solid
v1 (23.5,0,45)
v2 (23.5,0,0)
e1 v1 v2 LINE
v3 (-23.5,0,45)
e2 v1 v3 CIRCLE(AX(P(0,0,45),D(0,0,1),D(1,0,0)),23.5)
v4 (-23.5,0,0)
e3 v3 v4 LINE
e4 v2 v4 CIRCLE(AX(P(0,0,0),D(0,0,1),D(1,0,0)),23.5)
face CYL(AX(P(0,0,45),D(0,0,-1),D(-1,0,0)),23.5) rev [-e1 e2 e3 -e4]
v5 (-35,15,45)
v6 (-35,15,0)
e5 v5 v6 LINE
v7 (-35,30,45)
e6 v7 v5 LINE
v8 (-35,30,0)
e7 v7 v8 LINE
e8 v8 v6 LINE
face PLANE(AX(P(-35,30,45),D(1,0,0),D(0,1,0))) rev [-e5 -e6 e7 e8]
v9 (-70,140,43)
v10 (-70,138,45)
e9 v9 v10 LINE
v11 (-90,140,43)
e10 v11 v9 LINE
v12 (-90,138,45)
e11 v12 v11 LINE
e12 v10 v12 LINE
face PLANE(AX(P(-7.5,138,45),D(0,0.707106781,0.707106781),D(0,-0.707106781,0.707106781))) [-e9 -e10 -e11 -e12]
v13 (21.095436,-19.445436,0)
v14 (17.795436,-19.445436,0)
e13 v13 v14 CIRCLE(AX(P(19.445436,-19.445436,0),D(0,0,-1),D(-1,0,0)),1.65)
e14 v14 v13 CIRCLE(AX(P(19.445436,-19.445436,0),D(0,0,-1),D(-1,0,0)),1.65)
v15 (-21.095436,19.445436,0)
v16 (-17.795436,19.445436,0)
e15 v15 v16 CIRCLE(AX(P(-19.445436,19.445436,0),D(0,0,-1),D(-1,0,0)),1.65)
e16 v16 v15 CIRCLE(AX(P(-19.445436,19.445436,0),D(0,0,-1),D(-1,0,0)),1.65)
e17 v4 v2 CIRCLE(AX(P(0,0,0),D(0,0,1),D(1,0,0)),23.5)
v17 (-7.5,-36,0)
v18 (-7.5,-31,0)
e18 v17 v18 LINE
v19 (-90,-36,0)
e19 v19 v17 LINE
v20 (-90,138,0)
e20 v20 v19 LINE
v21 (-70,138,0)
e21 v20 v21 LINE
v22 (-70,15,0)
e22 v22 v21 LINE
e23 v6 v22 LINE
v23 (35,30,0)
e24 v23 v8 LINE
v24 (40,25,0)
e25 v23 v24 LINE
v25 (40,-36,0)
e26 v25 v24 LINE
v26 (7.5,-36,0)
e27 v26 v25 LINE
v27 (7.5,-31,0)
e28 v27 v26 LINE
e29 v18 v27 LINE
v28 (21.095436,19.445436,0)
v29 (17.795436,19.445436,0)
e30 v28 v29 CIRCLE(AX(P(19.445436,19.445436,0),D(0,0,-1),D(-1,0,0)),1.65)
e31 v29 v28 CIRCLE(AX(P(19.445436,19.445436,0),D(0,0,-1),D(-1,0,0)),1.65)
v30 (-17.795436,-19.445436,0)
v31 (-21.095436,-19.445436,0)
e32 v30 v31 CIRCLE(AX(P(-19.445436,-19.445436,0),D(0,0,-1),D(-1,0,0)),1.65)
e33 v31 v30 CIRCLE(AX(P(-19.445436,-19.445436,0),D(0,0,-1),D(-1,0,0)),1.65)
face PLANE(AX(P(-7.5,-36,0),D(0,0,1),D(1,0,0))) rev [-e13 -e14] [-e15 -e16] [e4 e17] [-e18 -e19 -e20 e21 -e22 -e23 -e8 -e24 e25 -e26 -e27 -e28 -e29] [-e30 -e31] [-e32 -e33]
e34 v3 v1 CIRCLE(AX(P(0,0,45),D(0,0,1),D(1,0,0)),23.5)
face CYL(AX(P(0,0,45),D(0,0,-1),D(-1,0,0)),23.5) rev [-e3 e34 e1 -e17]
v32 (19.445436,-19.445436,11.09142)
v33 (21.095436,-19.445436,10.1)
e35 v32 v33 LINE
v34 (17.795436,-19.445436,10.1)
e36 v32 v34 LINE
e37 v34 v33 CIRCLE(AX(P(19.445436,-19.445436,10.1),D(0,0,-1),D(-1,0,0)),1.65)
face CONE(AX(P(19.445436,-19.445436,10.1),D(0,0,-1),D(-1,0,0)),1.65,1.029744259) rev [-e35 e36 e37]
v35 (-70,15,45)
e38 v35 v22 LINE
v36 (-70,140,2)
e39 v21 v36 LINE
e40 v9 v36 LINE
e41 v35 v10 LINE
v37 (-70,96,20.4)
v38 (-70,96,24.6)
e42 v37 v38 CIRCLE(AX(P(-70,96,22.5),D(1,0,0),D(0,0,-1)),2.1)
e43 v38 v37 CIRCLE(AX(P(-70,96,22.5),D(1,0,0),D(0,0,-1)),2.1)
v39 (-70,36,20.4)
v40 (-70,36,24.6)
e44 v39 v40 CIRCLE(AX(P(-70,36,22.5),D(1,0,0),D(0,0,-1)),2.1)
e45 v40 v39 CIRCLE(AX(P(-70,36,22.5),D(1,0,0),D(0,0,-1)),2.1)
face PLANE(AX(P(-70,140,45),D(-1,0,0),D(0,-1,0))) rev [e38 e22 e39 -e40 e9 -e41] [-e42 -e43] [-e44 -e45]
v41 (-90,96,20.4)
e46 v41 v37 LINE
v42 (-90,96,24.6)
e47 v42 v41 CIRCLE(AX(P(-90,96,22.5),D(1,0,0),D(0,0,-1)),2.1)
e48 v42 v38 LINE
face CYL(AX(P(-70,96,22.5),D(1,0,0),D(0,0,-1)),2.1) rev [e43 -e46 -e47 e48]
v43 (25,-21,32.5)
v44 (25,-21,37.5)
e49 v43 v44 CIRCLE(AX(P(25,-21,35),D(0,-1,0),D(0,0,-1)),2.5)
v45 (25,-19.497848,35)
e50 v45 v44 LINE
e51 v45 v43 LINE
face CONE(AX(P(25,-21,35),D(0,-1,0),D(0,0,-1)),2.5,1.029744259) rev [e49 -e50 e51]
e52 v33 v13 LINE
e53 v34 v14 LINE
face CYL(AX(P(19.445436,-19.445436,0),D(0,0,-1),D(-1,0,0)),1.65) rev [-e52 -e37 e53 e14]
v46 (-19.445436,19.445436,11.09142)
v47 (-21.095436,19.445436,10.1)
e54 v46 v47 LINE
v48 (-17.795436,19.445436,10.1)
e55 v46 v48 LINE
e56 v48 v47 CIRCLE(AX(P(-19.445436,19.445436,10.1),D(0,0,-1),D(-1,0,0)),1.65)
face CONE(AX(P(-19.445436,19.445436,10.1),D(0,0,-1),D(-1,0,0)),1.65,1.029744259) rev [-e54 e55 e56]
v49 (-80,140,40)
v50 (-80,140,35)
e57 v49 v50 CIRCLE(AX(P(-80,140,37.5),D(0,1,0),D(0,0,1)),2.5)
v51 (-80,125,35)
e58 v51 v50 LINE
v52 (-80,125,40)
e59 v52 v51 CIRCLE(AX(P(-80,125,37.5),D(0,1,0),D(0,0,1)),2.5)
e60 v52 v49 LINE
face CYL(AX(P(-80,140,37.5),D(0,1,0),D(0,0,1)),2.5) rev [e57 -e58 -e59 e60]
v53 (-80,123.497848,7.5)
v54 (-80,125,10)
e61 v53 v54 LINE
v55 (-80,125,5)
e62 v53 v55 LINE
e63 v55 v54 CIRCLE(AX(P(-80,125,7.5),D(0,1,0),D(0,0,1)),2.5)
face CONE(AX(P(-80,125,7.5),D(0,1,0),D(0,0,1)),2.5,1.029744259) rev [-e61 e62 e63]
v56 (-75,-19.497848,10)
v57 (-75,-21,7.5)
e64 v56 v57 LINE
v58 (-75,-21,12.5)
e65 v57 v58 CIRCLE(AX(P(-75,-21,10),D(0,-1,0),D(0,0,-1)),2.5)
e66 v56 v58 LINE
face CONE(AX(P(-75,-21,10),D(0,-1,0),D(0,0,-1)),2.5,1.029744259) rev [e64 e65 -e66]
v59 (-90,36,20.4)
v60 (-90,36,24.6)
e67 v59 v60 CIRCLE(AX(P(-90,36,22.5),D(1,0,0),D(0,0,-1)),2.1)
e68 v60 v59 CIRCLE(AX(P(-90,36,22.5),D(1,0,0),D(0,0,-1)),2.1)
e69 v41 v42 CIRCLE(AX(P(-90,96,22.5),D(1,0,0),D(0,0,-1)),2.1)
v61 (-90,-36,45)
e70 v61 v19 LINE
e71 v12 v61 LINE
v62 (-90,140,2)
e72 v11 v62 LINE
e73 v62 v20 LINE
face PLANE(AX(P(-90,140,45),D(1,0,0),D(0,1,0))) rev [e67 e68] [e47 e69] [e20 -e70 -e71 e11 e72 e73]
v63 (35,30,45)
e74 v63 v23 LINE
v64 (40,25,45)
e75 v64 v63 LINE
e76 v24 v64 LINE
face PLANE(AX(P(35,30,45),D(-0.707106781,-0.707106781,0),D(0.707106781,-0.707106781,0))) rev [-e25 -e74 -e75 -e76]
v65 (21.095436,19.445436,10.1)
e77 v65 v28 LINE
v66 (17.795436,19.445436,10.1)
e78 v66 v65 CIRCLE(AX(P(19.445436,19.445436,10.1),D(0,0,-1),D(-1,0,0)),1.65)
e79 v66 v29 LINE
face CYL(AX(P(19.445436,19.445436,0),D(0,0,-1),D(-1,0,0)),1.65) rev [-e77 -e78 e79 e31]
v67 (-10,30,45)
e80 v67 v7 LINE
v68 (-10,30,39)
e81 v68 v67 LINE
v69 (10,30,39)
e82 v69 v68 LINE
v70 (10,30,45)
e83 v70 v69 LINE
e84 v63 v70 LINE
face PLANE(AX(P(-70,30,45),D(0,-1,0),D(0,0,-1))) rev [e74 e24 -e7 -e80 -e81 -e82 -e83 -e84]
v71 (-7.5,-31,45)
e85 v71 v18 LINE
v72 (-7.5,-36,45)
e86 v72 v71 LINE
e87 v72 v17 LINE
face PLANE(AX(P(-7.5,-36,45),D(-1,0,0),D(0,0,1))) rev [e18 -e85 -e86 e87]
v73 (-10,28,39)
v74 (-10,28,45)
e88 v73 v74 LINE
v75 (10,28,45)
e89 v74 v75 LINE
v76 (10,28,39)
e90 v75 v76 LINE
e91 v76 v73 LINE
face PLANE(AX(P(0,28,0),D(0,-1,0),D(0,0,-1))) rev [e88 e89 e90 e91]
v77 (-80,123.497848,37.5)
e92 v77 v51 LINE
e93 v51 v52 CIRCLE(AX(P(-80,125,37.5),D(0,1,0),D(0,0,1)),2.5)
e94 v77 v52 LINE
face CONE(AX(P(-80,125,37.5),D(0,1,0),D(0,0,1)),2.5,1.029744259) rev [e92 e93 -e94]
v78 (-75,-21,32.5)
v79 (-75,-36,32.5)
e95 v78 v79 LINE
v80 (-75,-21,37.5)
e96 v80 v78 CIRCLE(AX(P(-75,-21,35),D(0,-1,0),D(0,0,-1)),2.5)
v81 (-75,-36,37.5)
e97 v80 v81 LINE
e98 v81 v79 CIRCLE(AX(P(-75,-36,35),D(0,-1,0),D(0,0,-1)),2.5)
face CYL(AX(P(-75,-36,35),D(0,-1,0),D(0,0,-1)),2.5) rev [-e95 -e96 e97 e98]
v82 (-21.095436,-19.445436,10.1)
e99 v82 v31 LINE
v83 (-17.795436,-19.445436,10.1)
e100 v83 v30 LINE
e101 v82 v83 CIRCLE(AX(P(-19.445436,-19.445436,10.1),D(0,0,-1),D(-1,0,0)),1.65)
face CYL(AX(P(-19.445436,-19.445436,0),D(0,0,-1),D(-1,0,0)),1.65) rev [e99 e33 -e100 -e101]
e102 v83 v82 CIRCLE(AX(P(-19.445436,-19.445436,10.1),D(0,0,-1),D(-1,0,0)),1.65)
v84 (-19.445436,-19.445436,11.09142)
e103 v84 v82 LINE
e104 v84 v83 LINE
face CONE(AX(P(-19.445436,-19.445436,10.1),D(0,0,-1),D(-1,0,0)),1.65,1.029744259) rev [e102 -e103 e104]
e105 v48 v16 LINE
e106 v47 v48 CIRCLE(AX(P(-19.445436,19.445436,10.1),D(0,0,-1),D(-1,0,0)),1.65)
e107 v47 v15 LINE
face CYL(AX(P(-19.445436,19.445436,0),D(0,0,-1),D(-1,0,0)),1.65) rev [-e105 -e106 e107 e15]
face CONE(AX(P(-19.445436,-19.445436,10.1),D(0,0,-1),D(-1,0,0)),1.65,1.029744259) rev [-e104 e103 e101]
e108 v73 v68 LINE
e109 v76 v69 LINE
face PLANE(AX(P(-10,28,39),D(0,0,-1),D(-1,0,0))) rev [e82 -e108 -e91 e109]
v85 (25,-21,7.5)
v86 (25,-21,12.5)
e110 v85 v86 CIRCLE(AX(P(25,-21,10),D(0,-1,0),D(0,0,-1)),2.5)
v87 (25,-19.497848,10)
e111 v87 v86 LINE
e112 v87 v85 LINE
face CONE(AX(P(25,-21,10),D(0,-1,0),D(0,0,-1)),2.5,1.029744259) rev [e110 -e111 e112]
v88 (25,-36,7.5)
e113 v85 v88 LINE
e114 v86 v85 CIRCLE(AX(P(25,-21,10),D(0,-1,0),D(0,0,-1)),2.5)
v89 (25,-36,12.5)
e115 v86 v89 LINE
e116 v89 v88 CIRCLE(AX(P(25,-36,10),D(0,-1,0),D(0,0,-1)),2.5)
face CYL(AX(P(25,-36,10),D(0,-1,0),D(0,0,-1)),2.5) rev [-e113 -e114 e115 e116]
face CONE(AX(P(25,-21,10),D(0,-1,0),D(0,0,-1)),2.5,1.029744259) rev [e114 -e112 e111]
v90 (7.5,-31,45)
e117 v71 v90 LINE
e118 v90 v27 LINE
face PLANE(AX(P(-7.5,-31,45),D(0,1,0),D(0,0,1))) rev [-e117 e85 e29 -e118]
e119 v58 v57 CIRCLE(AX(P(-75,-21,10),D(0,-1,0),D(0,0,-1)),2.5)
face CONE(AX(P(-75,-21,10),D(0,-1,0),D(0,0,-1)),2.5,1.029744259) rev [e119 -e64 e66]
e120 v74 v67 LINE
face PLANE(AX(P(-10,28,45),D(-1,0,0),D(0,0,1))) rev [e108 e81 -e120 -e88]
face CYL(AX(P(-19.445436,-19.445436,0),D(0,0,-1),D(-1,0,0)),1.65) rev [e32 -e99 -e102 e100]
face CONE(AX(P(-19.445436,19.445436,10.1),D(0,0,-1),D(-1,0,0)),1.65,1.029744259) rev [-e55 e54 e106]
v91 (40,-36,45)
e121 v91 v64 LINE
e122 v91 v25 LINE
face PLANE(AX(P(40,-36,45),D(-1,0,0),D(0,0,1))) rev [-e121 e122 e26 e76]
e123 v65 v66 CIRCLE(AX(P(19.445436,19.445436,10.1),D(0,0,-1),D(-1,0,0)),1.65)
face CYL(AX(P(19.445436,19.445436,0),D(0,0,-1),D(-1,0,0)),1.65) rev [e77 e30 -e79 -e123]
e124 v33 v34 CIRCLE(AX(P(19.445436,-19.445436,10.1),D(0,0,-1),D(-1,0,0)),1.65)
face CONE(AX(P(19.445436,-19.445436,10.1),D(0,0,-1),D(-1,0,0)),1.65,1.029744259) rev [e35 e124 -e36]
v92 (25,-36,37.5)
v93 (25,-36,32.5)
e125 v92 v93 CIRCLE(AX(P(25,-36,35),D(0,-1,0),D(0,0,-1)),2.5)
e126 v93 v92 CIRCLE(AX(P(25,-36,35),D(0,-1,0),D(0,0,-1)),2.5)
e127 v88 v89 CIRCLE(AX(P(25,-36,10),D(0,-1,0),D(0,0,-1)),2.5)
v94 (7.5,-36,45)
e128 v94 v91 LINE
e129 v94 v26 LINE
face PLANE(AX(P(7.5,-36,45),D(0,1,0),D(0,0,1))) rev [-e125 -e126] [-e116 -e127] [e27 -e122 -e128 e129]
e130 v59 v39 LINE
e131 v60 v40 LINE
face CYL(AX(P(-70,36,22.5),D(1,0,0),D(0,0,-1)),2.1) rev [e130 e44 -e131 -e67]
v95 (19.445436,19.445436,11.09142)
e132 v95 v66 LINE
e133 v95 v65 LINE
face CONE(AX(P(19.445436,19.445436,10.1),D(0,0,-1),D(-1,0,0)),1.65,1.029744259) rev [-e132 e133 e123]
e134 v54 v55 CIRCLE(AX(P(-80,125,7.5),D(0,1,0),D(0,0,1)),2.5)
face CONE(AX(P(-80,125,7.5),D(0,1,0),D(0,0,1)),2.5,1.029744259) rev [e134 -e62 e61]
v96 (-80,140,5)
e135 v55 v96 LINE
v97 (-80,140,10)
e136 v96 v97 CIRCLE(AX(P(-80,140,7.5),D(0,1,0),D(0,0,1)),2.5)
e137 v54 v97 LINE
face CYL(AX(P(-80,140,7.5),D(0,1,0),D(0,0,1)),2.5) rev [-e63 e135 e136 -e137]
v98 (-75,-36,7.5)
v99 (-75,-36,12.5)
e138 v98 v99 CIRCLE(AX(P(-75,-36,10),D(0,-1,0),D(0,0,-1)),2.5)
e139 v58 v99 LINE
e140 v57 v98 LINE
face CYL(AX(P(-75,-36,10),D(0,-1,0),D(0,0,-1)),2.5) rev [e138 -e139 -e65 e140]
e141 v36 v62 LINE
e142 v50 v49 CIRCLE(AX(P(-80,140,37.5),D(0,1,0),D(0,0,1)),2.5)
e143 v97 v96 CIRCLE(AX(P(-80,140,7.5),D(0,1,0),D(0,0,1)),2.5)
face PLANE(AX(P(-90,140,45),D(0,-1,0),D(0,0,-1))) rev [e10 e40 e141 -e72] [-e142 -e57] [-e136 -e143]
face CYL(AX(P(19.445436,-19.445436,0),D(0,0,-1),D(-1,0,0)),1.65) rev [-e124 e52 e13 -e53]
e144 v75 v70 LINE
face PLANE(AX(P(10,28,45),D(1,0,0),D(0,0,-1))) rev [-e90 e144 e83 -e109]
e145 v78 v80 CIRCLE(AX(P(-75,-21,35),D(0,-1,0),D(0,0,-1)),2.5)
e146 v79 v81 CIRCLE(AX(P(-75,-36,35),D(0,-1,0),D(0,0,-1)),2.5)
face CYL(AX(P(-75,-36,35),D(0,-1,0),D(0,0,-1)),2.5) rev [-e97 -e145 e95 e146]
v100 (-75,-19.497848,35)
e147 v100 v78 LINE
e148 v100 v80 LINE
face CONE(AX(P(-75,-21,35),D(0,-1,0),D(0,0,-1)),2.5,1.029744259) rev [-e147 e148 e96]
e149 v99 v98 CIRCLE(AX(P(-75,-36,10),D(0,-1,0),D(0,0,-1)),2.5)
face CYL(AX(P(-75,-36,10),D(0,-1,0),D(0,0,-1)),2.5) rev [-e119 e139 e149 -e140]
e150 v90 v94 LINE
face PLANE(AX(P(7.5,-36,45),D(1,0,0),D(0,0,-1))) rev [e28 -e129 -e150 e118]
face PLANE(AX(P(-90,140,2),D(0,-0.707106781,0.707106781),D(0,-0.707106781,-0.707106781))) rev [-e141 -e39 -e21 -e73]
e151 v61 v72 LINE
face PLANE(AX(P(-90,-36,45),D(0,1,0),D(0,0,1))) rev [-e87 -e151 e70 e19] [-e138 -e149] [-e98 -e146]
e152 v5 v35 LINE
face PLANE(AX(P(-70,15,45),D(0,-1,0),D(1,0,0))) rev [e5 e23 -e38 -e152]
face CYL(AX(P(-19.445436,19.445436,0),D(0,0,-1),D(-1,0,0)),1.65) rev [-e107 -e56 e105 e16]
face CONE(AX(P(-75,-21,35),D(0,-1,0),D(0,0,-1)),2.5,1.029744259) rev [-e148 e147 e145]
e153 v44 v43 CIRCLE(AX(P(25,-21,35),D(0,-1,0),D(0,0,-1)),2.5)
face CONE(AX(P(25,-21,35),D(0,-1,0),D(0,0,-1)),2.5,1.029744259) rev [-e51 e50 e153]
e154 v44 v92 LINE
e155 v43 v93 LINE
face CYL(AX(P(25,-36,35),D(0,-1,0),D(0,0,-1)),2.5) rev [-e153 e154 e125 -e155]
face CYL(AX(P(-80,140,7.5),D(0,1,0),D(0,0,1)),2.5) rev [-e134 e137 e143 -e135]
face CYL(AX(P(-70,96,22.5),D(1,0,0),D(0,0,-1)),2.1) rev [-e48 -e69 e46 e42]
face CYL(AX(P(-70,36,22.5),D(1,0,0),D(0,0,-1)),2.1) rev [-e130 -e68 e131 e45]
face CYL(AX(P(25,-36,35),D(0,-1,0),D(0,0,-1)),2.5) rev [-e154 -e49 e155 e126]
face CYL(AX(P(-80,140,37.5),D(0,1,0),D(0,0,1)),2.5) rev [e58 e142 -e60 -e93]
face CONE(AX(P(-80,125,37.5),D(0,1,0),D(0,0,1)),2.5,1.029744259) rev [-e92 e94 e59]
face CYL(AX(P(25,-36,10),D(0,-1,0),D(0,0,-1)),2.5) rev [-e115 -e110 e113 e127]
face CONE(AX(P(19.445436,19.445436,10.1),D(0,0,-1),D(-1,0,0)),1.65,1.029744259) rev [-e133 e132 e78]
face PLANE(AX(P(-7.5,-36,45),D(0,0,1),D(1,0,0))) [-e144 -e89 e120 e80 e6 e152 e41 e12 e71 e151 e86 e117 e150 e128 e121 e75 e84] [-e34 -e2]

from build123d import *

# Parameters (mm, degrees)
SKETCH1_R             = 23.5
BOSS_EXTRUDE1_DEPTH   = 45
M6_TAPPED_HOLE1_D     = 5
M6_TAPPED_HOLE1_DEPTH = 15
M6_TAPPED_HOLE1_TIP   = 1.502151548
M5_TAPPED_HOLE1_D     = 4.2
M6_TAPPED_HOLE2_D     = 5
M6_TAPPED_HOLE2_DEPTH = 15
M6_TAPPED_HOLE2_TIP   = 1.502151548
M4_TAPPED_HOLE1_D     = 3.3
M4_TAPPED_HOLE1_DEPTH = 10.1
M4_TAPPED_HOLE1_TIP   = 0.991420021
CHAMFER1_SIZE         = 5
CHAMFER2_SIZE         = 2
SKETCH18_W            = 35
SKETCH18_H            = 15
CUT_EXTRUDE1_DEPTH    = 173.409396496
SKETCH19_W            = 20
SKETCH19_H            = 6
CUT_EXTRUDE2_DEPTH    = 2


with BuildPart() as part:
    # Sketch1 → Boss-Extrude1 (new body)
    with BuildSketch(Plane.XY):
        Polygon((-90, 140), (-90, -36), (-7.5, -36), (-7.5, -31), (7.5, -31), (7.5, -36), (40, -36), (40, 30), (-70, 30), (-70, 140), align=None)
        with Locations(Location((0, 0, 0), (0, 0, 180))):
            Circle(SKETCH1_R, mode=Mode.SUBTRACT)
    extrude(amount=BOSS_EXTRUDE1_DEPTH)

    # M6 Tapped Hole1
    with Locations(Plane.XZ.offset(36)):
        with Locations((-75, 10), (25, 10), (-75, 35), (25, 35)):
            Hole(M6_TAPPED_HOLE1_D / 2, depth=M6_TAPPED_HOLE1_DEPTH)
            with Locations((0, 0, -(M6_TAPPED_HOLE1_DEPTH + M6_TAPPED_HOLE1_TIP / 2))):  # 118° drill point
                Cone(0, M6_TAPPED_HOLE1_D / 2, M6_TAPPED_HOLE1_TIP, mode=Mode.SUBTRACT)

    # M5 Tapped Hole1 (through all)
    with Locations(Plane(origin=(-70, 0, 0), x_dir=(0, 0, -1), z_dir=(1, 0, 0))):
        with Locations((-22.5, 96), (-22.5, 36)):
            Hole(M5_TAPPED_HOLE1_D / 2)

    # M6 Tapped Hole2
    with Locations(Plane(origin=(0, 140, 0), x_dir=(-1, 0, 0), z_dir=(0, 1, 0))):
        with Locations((80, 7.5), (80, 37.5)):
            Hole(M6_TAPPED_HOLE2_D / 2, depth=M6_TAPPED_HOLE2_DEPTH)
            with Locations((0, 0, -(M6_TAPPED_HOLE2_DEPTH + M6_TAPPED_HOLE2_TIP / 2))):  # 118° drill point
                Cone(0, M6_TAPPED_HOLE2_D / 2, M6_TAPPED_HOLE2_TIP, mode=Mode.SUBTRACT)

    # M4 Tapped Hole1
    with Locations(Plane(origin=(0, 0, 0), x_dir=(-1, 0, 0), z_dir=(0, 0, -1))):
        with Locations((-19.445436483, 19.445436483), (19.445436483, -19.445436483), (-19.445436483, -19.445436483), (19.445436483, 19.445436483)):
            Hole(M4_TAPPED_HOLE1_D / 2, depth=M4_TAPPED_HOLE1_DEPTH)
            with Locations((0, 0, -(M4_TAPPED_HOLE1_DEPTH + M4_TAPPED_HOLE1_TIP / 2))):  # 118° drill point
                Cone(0, M4_TAPPED_HOLE1_D / 2, M4_TAPPED_HOLE1_TIP, mode=Mode.SUBTRACT)

    # Chamfer1
    chamfer1_edges = [part.edges().sort_by_distance(p)[0] for p in [
        (40, 30, 22.5),
    ]]
    chamfer(chamfer1_edges, length=CHAMFER1_SIZE)

    # Chamfer2
    chamfer2_edges = [part.edges().sort_by_distance(p)[0] for p in [
        (-80, 140, 45),
        (-80, 140, 0),
    ]]
    chamfer(chamfer2_edges, length=CHAMFER2_SIZE)

    # Sketch18 → Cut-Extrude1 (cut, through all)
    with BuildSketch(Plane(origin=(0, 0, 0), x_dir=(-1, 0, 0), z_dir=(0, 0, -1))):
        with Locations((52.5, 22.5)):
            Rectangle(SKETCH18_W, SKETCH18_H)
    extrude(amount=-CUT_EXTRUDE1_DEPTH, mode=Mode.SUBTRACT)

    # Sketch19 → Cut-Extrude2 (cut)
    with BuildSketch(Plane(origin=(0, 30, 0), x_dir=(1, 0, 0), z_dir=(0, 1, 0))):
        with Locations((0, -42)):
            Rectangle(SKETCH19_W, SKETCH19_H)
    extrude(amount=-CUT_EXTRUDE2_DEPTH, mode=Mode.SUBTRACT)


solid = part.part
